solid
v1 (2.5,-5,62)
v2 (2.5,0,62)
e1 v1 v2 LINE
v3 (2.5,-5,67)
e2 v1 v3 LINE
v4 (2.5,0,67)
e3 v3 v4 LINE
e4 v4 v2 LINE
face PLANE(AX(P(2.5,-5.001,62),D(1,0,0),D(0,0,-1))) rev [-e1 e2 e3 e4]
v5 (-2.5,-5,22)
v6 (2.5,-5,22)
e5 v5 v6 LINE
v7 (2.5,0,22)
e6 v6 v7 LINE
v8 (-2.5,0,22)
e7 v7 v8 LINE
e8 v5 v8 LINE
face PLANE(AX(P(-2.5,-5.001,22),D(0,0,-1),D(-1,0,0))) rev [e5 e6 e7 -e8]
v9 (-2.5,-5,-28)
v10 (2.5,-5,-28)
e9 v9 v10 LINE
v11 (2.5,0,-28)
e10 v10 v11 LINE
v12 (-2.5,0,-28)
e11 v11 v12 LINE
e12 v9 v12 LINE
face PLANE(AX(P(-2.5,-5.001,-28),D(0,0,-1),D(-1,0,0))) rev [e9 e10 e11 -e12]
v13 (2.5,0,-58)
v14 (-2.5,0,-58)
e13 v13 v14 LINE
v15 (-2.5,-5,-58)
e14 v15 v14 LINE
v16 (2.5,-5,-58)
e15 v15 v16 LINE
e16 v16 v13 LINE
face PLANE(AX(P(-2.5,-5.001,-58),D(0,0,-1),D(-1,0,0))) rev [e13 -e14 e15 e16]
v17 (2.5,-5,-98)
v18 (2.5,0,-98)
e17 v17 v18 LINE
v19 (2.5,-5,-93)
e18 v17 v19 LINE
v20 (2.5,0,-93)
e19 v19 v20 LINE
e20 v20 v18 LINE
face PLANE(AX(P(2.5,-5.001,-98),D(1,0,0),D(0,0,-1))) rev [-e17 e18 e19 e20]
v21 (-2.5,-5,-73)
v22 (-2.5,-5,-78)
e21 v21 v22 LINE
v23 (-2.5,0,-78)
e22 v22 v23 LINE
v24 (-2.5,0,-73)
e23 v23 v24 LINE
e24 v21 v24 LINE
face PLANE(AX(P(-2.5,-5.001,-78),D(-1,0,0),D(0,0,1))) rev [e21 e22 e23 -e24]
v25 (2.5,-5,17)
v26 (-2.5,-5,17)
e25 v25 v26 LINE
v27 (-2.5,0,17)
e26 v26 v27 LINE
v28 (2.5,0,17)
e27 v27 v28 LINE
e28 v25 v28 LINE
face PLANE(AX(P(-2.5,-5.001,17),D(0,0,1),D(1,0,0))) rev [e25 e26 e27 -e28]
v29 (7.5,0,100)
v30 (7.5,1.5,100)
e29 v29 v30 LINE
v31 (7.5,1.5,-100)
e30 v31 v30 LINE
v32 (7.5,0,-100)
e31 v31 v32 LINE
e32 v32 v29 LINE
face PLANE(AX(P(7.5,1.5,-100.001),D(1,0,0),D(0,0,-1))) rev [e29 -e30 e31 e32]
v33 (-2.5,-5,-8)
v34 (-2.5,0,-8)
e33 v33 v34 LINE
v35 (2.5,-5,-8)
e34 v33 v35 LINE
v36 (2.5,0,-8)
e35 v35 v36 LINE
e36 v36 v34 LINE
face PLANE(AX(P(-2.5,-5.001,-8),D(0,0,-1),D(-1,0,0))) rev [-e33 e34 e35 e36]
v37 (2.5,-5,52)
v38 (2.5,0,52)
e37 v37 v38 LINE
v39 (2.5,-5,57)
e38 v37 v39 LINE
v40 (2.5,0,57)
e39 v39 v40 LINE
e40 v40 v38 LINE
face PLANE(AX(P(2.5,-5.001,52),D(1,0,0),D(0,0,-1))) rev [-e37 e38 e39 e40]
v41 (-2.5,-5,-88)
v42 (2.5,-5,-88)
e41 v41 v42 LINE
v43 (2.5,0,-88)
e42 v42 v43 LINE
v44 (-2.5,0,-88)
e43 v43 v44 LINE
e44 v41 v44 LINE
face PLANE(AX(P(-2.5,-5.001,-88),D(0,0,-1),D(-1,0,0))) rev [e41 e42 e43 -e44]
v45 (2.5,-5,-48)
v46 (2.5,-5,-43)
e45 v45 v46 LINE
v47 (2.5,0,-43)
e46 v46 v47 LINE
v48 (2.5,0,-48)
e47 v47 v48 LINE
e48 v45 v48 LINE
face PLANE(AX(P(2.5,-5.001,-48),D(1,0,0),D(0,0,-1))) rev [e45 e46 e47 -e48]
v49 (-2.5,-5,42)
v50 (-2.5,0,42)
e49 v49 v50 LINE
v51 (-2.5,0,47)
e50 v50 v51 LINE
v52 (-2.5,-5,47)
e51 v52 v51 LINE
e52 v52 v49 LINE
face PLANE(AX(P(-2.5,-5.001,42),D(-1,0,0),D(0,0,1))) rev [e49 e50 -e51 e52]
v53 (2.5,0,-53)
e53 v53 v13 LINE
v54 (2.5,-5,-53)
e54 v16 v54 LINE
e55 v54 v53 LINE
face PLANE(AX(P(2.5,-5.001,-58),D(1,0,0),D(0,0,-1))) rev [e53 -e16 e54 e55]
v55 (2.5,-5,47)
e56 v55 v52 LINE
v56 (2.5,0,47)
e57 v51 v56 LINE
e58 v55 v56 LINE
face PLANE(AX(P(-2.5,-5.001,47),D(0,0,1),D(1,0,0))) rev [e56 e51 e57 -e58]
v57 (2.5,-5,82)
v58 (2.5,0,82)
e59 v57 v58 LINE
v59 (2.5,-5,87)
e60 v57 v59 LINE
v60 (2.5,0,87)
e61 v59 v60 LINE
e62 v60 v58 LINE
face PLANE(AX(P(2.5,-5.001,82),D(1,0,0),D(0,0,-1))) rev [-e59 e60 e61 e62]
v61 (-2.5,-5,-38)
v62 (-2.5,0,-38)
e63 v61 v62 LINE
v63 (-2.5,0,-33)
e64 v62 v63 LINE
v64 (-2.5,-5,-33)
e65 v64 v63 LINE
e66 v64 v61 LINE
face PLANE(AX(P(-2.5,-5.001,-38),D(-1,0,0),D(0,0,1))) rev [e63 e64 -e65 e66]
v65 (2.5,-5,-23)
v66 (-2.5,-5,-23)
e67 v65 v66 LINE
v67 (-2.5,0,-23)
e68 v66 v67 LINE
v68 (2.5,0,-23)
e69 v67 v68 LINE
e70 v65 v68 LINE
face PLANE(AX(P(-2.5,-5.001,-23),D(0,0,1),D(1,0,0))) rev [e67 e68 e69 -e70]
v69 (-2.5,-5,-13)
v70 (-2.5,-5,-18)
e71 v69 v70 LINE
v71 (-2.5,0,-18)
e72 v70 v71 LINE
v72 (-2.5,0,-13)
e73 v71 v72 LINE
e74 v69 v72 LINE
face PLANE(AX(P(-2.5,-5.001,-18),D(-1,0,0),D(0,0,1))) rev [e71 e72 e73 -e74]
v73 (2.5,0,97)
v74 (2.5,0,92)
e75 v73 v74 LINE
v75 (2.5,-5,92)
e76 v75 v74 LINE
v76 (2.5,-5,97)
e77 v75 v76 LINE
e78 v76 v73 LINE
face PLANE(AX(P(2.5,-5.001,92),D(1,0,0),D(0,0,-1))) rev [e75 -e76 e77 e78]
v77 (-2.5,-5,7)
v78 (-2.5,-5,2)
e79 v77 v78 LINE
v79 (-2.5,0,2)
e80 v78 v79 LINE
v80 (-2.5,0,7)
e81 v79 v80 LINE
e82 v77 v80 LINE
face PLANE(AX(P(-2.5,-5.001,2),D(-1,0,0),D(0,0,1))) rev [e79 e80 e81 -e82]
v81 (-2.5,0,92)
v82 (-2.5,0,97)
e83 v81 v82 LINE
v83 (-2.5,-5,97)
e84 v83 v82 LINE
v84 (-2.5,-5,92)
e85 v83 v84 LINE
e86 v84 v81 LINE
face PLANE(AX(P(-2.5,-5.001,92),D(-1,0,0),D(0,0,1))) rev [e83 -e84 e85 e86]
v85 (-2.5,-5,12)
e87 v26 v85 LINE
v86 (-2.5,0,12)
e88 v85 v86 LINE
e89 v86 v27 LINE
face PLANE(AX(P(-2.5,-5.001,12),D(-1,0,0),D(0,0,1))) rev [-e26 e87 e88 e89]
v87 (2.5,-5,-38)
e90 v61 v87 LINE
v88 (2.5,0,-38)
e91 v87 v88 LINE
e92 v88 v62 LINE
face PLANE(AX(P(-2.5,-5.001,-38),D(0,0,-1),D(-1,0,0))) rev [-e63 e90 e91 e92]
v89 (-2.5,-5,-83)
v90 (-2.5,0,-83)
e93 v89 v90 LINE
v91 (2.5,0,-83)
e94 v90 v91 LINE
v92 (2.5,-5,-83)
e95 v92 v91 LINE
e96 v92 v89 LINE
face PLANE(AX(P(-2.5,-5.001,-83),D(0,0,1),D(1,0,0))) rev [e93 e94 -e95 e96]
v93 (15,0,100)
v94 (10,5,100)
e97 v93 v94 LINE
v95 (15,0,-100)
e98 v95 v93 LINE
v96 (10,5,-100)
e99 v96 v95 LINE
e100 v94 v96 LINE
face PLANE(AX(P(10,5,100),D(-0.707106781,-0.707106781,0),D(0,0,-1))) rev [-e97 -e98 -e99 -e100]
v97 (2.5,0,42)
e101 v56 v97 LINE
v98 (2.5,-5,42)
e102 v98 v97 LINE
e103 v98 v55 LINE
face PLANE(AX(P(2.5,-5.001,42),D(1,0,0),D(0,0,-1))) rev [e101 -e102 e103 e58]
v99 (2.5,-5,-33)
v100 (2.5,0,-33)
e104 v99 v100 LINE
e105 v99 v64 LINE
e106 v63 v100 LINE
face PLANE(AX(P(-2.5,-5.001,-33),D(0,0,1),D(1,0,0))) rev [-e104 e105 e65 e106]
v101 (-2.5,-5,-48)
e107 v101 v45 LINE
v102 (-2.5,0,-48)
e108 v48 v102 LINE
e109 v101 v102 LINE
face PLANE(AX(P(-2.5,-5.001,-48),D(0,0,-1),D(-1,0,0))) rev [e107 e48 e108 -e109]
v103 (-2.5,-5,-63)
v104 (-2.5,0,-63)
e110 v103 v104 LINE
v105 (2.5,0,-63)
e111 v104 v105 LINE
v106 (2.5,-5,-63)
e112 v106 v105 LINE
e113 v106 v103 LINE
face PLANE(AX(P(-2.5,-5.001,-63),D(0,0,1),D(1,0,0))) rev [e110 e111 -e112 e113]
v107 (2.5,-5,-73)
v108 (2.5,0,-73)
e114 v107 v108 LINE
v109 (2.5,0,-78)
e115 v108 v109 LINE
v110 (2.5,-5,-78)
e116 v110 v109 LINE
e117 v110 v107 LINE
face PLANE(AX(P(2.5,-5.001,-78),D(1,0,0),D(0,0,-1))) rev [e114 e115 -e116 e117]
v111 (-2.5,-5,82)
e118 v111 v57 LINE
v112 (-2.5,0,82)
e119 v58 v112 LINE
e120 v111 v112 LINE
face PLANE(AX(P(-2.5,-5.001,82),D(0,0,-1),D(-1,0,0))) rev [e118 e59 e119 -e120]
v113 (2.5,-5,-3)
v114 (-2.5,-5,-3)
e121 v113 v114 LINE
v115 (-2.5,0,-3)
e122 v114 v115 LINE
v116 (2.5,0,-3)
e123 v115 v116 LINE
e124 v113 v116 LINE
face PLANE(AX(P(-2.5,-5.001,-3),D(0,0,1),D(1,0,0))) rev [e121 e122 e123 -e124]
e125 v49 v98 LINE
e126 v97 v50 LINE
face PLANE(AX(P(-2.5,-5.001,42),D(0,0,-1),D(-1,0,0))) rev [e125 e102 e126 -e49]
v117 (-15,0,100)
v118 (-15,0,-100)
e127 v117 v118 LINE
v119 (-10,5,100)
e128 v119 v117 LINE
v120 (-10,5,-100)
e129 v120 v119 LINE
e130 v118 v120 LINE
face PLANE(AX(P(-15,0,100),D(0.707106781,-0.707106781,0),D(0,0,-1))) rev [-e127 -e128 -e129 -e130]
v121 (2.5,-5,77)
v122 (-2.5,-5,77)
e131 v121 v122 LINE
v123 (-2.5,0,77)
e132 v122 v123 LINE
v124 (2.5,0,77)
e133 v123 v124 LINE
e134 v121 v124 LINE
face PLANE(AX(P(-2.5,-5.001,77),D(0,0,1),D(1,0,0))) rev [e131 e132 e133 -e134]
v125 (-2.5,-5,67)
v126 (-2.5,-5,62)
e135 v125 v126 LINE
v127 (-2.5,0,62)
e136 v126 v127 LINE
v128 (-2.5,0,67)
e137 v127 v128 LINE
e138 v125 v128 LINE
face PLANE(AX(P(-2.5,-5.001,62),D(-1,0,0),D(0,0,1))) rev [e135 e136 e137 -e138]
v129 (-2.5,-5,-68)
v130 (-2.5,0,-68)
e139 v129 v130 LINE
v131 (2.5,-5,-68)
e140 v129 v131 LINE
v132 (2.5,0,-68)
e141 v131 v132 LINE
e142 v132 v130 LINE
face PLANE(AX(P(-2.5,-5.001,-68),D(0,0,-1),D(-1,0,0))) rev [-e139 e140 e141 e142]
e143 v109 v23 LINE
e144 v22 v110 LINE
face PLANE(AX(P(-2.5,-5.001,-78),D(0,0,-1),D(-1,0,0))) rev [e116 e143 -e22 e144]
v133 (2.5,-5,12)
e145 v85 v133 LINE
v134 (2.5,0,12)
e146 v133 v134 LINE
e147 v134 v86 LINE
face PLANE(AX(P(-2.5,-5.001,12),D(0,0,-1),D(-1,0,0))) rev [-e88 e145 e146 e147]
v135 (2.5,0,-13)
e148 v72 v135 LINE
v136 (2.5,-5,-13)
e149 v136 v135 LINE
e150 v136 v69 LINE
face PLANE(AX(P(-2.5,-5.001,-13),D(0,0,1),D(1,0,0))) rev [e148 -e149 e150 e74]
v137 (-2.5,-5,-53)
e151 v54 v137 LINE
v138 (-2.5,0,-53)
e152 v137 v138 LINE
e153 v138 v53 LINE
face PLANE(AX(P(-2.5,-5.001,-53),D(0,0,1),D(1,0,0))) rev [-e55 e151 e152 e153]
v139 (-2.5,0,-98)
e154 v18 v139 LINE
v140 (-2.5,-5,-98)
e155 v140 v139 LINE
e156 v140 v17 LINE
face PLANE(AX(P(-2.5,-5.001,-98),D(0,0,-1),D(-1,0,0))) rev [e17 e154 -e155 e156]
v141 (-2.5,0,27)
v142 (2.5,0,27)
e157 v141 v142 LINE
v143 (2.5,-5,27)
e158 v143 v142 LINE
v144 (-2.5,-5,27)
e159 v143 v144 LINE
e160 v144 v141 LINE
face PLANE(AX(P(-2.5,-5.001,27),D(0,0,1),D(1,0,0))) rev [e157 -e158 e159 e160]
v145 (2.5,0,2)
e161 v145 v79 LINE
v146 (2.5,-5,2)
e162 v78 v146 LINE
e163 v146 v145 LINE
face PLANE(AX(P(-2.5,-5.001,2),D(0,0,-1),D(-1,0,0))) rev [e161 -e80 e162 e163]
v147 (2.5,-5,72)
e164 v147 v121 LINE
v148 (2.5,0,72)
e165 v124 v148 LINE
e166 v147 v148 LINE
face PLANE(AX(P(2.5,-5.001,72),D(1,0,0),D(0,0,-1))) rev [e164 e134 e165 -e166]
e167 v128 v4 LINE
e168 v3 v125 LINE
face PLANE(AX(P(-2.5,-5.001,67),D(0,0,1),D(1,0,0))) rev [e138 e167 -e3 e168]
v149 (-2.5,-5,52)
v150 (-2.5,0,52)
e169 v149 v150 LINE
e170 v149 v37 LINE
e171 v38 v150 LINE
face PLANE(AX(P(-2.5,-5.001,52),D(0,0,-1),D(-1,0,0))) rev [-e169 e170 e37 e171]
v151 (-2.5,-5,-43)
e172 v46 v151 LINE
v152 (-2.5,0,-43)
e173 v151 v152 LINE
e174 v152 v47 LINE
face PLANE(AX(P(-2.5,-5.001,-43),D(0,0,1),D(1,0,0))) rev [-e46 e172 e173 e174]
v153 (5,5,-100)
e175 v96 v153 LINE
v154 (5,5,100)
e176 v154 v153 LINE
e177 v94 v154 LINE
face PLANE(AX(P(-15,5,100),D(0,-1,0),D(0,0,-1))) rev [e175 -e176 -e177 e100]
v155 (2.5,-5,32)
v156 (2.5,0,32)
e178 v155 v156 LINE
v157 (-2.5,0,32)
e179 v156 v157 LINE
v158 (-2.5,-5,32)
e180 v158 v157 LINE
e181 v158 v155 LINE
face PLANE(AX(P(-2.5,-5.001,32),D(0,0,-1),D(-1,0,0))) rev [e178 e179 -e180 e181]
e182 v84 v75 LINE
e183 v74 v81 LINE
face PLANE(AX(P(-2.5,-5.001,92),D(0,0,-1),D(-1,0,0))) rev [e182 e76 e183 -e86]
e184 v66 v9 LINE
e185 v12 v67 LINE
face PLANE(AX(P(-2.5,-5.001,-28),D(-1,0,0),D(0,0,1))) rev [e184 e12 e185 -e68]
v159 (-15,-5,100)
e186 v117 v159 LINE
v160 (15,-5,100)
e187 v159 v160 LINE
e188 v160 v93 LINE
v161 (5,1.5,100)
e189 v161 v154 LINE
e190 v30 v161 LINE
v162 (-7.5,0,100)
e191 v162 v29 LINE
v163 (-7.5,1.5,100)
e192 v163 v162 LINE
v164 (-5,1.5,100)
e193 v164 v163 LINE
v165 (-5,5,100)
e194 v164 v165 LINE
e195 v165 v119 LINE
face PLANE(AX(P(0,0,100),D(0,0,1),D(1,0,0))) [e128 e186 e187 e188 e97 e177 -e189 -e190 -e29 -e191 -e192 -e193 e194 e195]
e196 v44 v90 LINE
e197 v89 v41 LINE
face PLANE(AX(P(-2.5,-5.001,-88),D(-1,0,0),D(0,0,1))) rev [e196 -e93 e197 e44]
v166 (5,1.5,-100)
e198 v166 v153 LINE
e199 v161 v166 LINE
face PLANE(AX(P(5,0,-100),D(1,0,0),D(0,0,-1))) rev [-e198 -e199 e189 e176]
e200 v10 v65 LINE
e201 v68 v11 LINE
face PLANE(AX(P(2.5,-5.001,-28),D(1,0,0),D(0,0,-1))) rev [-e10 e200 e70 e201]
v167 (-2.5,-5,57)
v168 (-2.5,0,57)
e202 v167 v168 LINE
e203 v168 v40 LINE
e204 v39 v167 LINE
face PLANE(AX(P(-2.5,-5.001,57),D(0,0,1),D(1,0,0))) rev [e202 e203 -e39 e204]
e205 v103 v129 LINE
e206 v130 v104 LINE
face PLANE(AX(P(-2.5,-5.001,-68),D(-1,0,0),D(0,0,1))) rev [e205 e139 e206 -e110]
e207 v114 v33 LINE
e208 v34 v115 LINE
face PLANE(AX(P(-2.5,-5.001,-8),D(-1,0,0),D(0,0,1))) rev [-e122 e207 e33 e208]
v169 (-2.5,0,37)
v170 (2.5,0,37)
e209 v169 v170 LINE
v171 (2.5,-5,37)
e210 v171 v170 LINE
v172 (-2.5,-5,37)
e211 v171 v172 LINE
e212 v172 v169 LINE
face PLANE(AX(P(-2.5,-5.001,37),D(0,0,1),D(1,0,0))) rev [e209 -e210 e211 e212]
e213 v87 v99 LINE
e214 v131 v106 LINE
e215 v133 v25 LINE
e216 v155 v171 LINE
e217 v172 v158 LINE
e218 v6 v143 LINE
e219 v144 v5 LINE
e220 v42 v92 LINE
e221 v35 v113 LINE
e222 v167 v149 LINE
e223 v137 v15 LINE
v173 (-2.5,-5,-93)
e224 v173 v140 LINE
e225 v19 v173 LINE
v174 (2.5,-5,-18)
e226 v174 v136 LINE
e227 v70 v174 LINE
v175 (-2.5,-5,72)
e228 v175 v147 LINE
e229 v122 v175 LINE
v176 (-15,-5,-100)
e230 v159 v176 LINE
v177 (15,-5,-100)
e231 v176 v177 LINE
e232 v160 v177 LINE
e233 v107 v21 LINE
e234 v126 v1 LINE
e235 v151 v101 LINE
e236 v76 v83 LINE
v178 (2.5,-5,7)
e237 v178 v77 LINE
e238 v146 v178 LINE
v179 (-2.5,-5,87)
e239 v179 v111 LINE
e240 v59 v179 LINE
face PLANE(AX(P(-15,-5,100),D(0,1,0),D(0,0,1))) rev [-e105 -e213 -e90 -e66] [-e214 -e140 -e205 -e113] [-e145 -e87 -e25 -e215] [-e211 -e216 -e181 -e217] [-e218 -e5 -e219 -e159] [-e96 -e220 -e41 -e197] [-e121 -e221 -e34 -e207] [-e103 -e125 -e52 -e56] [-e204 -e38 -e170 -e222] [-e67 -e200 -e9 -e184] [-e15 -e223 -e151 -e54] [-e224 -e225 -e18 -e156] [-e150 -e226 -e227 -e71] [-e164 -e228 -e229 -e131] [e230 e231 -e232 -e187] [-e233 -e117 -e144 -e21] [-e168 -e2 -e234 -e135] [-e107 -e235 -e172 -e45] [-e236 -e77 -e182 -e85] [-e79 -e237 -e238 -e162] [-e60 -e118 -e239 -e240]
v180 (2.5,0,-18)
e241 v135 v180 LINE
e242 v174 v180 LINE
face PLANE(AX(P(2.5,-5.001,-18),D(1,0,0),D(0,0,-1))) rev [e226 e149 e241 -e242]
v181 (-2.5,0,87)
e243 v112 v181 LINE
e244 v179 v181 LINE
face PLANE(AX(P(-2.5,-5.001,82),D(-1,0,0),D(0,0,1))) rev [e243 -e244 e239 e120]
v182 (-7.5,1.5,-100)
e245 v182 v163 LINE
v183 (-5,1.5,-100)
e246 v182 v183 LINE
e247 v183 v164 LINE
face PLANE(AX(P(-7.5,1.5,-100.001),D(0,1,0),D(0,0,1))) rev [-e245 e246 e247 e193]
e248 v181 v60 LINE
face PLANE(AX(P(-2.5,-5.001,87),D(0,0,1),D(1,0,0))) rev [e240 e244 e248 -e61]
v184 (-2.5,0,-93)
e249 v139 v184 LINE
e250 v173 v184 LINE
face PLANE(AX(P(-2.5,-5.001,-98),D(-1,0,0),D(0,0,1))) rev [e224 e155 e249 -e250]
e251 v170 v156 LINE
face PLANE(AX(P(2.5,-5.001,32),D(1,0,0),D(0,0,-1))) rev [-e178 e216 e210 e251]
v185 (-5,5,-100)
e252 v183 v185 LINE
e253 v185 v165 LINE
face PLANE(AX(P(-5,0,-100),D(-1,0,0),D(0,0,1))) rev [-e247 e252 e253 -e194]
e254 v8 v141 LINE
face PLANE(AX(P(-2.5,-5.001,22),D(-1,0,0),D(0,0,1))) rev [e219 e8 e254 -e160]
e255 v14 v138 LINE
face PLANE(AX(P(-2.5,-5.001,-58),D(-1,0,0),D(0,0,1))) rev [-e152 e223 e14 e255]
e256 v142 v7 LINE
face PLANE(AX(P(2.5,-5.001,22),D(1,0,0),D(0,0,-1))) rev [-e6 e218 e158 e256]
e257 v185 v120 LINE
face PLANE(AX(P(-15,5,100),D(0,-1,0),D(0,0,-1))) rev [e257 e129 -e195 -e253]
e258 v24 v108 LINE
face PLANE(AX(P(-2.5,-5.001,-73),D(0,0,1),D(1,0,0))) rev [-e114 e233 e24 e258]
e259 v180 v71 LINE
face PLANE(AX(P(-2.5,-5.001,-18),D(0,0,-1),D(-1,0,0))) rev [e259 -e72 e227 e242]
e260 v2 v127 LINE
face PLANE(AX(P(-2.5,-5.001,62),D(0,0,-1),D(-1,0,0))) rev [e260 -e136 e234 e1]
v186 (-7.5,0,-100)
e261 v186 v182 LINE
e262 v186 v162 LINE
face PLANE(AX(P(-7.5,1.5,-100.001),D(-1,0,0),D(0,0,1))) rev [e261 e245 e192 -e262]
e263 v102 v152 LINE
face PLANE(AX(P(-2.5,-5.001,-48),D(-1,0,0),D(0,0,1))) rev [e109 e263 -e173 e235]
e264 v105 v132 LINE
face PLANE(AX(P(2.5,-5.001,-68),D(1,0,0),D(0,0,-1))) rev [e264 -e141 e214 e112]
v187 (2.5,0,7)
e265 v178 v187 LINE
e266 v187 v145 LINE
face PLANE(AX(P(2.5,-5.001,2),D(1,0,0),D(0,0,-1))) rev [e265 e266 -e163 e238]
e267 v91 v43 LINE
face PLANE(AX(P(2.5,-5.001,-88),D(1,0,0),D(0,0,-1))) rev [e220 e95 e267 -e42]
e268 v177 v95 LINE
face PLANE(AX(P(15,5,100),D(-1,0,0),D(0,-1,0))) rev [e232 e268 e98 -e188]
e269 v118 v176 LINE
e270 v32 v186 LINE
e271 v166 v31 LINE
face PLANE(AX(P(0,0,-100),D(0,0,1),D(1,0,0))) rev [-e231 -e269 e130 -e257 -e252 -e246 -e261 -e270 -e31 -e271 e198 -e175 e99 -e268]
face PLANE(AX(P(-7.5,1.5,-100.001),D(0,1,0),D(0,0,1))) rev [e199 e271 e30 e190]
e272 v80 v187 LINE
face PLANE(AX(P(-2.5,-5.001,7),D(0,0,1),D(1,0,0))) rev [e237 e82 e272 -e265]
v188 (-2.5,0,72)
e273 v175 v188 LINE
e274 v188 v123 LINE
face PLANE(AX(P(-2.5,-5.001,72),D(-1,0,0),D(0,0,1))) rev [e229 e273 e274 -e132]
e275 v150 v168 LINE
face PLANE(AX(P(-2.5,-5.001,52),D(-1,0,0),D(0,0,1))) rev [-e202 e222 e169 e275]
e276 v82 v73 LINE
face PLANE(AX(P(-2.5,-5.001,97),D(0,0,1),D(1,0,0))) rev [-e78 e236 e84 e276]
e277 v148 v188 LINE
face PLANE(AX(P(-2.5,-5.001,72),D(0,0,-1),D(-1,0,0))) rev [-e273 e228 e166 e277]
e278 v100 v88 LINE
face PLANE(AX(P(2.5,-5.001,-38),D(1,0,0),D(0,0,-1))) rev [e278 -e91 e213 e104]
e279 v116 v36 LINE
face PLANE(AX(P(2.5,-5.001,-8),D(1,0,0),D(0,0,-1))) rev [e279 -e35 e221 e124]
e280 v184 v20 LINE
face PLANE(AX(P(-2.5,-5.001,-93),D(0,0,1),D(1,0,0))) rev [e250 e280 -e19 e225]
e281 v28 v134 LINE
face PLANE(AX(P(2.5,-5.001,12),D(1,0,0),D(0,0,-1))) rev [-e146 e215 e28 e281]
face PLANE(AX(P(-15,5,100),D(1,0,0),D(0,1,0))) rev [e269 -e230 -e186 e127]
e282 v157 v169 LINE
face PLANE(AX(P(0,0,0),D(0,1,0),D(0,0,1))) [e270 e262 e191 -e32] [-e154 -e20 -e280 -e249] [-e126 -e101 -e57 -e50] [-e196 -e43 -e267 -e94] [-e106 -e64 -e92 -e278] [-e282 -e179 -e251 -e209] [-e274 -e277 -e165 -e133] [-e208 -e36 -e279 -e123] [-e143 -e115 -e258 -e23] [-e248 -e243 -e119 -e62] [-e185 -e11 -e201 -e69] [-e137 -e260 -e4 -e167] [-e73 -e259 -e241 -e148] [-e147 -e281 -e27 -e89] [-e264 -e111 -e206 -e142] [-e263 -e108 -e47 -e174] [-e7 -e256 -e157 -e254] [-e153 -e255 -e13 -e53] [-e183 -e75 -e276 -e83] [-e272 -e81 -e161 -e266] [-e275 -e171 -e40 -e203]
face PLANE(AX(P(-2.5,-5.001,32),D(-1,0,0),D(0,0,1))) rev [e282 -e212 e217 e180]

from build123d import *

# Parameters (mm, degrees)
TRACK_PROFILE_SKETCH_W            = 30
TRACK_PROFILE_SKETCH_H            = 10
TRACK_BODY_200MM_DEPTH            = 100
EDGE_CHAMFER_5MM_SIZE             = 5
GUIDE_GROOVE_SKETCH_W             = 10
GUIDE_GROOVE_SKETCH_H             = 200
GUIDE_GROOVE_10X5_DEPTH           = 5
END_START                         = -200
END_NOTCH_SKETCH_W                = 15
END_NOTCH_SKETCH_H                = 1.5
END_NOTCH_CUT_DEPTH               = 200
RACK_POCKET_CUT_REACH             = 103.242
RACK_POCKET_SKETCH_W              = 5
RACK_POCKET_SKETCH_H              = 5
RACK_POCKET_PATTERN_20X10MM_COUNT = 20
RACK_POCKET_PATTERN_20X10MM_PITCH = 10


with BuildPart() as part:
    # Track Profile Sketch → Track Body 200mm (new, symmetric)
    with BuildSketch(Plane.XY):
        Rectangle(TRACK_PROFILE_SKETCH_W, TRACK_PROFILE_SKETCH_H)
    extrude(amount=TRACK_BODY_200MM_DEPTH, both=True)

    # Edge Chamfer 5mm
    edge_chamfer_5mm_edges = [part.edges().sort_by_distance(p)[0] for p in [
        (-15, 5, 0),
        (15, 5, 0),
    ]]
    chamfer(edge_chamfer_5mm_edges, length=EDGE_CHAMFER_5MM_SIZE)

    # Guide Groove Sketch → Guide Groove 10x5 (cut)
    with BuildSketch(Plane(origin=(0, 5, 0), x_dir=(1, 0, 0), z_dir=(0, 1, 0))):
        Rectangle(GUIDE_GROOVE_SKETCH_W, GUIDE_GROOVE_SKETCH_H)
    extrude(amount=-GUIDE_GROOVE_10X5_DEPTH, mode=Mode.SUBTRACT)

    # End Notch Sketch → End Notch Cut (cut)
    with BuildSketch(Plane.XY.offset(100).offset(END_START)):
        with Locations((0, 0.75)):
            Rectangle(END_NOTCH_SKETCH_W, END_NOTCH_SKETCH_H)
    extrude(amount=END_NOTCH_CUT_DEPTH, mode=Mode.SUBTRACT)

    # Rack Pocket Sketch → Rack Pocket Cut (cut, up to next)
    with BuildSketch(Plane(origin=(0, 0, 0), x_dir=(1, 0, 0), z_dir=(0, 1, 0)), mode=Mode.PRIVATE) as rack_pocket_cut_sk1:
        with Locations((0, 95.5)):
            Rectangle(RACK_POCKET_SKETCH_W, RACK_POCKET_SKETCH_H)
    rack_pocket_cut_tool1 = extrude(rack_pocket_cut_sk1.sketch, amount=-RACK_POCKET_CUT_REACH, mode=Mode.PRIVATE) & part.part
    rack_pocket_cut = rack_pocket_cut_tool1.solids().sort_by_distance((0, 0, -95.5))[0]
    add(rack_pocket_cut, mode=Mode.SUBTRACT)

    # Rack Pocket Pattern 20x10mm: Rack Pocket Cut ×20
    with Locations(*[(0, 0, i * RACK_POCKET_PATTERN_20X10MM_PITCH) for i in range(1, RACK_POCKET_PATTERN_20X10MM_COUNT)]):
        add(rack_pocket_cut, mode=Mode.SUBTRACT)


solid = part.part
